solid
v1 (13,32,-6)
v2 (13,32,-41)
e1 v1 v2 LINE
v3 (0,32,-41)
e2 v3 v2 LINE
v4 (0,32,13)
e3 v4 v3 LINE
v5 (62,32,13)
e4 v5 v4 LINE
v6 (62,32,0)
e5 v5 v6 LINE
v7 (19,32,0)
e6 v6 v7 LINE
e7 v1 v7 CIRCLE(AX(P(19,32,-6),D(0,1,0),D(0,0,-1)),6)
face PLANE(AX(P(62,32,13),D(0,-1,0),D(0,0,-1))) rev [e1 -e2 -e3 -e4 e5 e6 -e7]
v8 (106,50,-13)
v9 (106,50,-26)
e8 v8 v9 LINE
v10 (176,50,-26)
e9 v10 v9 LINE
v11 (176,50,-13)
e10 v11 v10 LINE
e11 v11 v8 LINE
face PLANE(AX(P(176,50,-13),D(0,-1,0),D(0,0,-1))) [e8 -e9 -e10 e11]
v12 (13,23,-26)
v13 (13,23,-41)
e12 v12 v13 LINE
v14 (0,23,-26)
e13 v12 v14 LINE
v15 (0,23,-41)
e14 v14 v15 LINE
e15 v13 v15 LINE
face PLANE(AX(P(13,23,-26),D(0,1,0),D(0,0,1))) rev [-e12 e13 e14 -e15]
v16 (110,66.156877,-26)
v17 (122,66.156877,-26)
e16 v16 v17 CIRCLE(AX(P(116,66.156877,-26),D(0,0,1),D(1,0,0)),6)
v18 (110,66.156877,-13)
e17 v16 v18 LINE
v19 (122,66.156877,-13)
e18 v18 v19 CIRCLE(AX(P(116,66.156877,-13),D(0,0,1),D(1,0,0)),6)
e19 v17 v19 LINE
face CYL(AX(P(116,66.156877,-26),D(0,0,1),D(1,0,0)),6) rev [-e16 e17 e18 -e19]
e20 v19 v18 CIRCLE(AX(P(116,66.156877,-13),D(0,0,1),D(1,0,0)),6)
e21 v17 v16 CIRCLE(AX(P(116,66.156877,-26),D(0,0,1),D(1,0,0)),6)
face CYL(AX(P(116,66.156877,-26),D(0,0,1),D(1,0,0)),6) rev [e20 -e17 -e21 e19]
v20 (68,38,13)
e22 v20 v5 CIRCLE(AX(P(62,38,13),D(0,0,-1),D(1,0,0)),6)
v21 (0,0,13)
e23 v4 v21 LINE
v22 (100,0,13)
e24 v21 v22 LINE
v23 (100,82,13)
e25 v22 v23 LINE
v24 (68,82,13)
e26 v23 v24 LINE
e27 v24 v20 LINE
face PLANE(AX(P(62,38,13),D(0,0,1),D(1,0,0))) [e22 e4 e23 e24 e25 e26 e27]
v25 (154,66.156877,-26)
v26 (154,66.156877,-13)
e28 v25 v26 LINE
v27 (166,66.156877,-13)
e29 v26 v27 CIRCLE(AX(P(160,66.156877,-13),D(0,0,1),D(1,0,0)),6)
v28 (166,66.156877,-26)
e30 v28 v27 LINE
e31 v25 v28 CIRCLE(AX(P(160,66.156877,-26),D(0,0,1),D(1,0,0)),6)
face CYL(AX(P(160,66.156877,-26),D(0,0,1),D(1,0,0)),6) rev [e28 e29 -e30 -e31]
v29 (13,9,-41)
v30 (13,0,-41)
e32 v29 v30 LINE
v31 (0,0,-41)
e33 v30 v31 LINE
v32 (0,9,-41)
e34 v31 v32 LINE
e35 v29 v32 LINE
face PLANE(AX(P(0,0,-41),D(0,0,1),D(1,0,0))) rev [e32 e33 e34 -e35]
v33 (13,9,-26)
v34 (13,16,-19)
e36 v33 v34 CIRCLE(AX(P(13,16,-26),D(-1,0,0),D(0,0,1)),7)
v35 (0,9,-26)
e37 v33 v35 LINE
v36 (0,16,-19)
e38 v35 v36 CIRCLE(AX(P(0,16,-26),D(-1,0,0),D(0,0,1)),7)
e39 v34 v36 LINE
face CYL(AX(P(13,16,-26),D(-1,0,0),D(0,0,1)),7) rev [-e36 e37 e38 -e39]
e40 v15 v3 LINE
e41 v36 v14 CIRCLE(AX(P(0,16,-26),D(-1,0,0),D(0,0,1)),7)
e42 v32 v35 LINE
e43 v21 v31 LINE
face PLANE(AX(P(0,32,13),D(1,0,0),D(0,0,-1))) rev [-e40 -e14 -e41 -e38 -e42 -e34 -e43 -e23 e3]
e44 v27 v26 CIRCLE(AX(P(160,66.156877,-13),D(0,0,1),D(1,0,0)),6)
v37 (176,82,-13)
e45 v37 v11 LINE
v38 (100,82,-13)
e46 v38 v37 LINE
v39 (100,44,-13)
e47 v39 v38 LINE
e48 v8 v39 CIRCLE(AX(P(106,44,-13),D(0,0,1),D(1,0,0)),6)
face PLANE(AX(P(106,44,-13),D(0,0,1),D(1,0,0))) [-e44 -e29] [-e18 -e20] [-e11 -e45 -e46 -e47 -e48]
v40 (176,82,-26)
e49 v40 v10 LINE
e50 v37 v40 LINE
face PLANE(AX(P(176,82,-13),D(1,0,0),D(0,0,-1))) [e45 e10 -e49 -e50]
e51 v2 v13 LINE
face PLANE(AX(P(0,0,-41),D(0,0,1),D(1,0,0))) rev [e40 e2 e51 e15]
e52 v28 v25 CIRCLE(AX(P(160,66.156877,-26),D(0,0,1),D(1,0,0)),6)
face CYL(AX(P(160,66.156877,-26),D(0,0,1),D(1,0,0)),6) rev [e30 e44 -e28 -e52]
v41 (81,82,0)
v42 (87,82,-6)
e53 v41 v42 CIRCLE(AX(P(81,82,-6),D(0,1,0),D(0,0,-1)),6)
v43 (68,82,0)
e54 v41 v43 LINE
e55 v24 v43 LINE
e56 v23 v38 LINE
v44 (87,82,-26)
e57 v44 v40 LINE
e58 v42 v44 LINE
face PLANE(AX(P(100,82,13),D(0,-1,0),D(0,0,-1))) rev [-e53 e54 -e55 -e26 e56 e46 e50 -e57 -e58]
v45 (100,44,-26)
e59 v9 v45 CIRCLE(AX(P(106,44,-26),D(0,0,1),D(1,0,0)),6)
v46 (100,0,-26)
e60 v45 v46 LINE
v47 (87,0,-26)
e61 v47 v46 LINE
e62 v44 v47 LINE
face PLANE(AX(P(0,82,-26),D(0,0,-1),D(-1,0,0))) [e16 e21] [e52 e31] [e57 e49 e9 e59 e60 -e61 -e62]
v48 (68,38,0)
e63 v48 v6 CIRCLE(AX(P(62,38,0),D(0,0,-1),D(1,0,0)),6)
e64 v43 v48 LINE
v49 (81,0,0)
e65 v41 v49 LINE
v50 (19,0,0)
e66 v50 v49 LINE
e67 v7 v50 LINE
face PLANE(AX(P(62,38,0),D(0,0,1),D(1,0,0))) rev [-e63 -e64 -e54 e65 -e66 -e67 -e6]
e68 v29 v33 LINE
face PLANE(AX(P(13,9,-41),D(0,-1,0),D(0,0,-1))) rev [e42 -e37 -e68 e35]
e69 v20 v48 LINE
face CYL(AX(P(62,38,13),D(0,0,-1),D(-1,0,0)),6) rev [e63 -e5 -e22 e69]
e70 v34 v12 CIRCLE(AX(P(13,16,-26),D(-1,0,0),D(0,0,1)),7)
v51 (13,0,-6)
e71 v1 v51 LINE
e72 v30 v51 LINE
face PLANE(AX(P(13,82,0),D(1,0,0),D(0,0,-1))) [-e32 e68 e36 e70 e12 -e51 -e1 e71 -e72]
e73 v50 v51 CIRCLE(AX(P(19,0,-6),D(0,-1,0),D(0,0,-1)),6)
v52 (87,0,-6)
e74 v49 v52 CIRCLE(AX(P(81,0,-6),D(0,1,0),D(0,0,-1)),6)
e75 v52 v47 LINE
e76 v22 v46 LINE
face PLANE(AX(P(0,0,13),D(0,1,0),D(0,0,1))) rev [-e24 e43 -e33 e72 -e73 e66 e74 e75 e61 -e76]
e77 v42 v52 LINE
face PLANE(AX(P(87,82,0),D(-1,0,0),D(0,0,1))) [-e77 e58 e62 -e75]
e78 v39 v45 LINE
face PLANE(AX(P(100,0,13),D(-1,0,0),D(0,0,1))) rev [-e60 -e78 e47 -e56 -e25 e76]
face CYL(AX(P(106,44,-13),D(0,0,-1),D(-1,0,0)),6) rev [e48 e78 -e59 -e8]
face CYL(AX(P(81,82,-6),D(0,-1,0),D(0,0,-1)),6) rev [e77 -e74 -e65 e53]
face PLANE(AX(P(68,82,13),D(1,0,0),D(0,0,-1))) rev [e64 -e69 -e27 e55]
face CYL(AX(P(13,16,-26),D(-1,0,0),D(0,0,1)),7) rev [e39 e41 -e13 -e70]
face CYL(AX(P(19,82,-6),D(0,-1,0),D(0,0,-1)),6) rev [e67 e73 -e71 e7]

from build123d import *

# Parameters (mm, degrees)
BASE_PROFILE_13MM_DEPTH    = 13
UPRIGHT_BLOCK_82MM_DEPTH   = 82
RECTANGULAR_CUT_SKETCH_W   = 54
RECTANGULAR_CUT_SKETCH_H   = 50
RECTANGULAR_CUT_20MM_DEPTH = 20
POCKET_CUT_SKETCH_W        = 13
POCKET_CUT_SKETCH_H        = 32
POCKET_CUT_13MM_DEPTH      = 13
SLOT_CUT_14MM_DEPTH        = 13
MOUNTING_FLANGE_6MM_DEPTH  = 13
FLANGE_HOLES_SKETCH_R      = 6
FLANGE_HOLES_2X_12_DEPTH   = 13


with BuildPart() as part:
    # Base Profile Sketch → Base Profile 13mm (new body)
    with BuildSketch(Plane.XY):
        with BuildLine():
            Line((0, 0), (100, 0))
            Line((100, 0), (100, 82))
            Line((100, 82), (68, 82))
            Line((68, 82), (68, 38))
            ThreePointArc((68, 38), (66.242640687, 33.757359313), (62, 32))
            Line((62, 32), (0, 32))
            Line((0, 32), (0, 0))
        make_face()
    extrude(amount=BASE_PROFILE_13MM_DEPTH)

    # Upright Block Sketch → Upright Block 82mm (add)
    with BuildSketch(Plane.XZ):
        with BuildLine():
            Line((19, 0), (0, 0))
            Line((0, 0), (0, -54))
            Line((0, -54), (13, -54))
            Line((13, -54), (13, -6))
            ThreePointArc((13, -6), (14.757359313, -1.757359313), (19, 0))
        make_face()
        with BuildLine():
            Line((100, 0), (81, 0))
            ThreePointArc((81, 0), (85.242640687, -1.757359313), (87, -6))
            Line((87, -6), (87, -26))
            Line((87, -26), (100, -26))
            Line((100, -26), (100, 0))
        make_face()
    extrude(amount=-UPRIGHT_BLOCK_82MM_DEPTH)

    # Rectangular Cut Sketch → Rectangular Cut 20mm (cut)
    with BuildSketch(Plane.ZY):
        with Locations((-27, 57)):
            Rectangle(RECTANGULAR_CUT_SKETCH_W, RECTANGULAR_CUT_SKETCH_H)
    extrude(amount=-RECTANGULAR_CUT_20MM_DEPTH, mode=Mode.SUBTRACT)

    # Pocket Cut Sketch → Pocket Cut 13mm (cut)
    with BuildSketch(Plane(origin=(0, 0, -54), x_dir=(-1, 0, 0), z_dir=(0, 0, -1))):
        with Locations((-6.5, 16)):
            Rectangle(POCKET_CUT_SKETCH_W, POCKET_CUT_SKETCH_H)
    extrude(amount=-POCKET_CUT_13MM_DEPTH, mode=Mode.SUBTRACT)

    # Slot Cut Sketch → Slot Cut 14mm (cut)
    with BuildSketch(Plane.ZY):
        with BuildLine():
            Line((-41, 9), (-26, 9))
            ThreePointArc((-26, 9), (-19, 16), (-26, 23))
            Line((-26, 23), (-41, 23))
            Line((-41, 23), (-41, 9))
        make_face()
    extrude(amount=-SLOT_CUT_14MM_DEPTH, mode=Mode.SUBTRACT)

    # Mounting Flange Sketch → Mounting Flange 6mm (add)
    with BuildSketch(Plane(origin=(0, 0, -26), x_dir=(-1, 0, 0), z_dir=(0, 0, -1))):
        with BuildLine():
            Line((-100, 82), (-176, 82))
            Line((-176, 82), (-176, 50))
            Line((-176, 50), (-106, 50))
            ThreePointArc((-106, 50), (-101.757359313, 48.242640687), (-100, 44))
            Line((-100, 44), (-100, 82))
        make_face()
    extrude(amount=-MOUNTING_FLANGE_6MM_DEPTH)

    # Flange Holes Sketch → Flange Holes 2xØ12 (cut)
    with BuildSketch(Plane.XY.offset(-13)):
        with Locations((116, 66.156876682)):
            Circle(FLANGE_HOLES_SKETCH_R)
        with Locations((160, 66.156876682)):
            Circle(FLANGE_HOLES_SKETCH_R)
    extrude(amount=-FLANGE_HOLES_2X_12_DEPTH, mode=Mode.SUBTRACT)


solid = part.part
